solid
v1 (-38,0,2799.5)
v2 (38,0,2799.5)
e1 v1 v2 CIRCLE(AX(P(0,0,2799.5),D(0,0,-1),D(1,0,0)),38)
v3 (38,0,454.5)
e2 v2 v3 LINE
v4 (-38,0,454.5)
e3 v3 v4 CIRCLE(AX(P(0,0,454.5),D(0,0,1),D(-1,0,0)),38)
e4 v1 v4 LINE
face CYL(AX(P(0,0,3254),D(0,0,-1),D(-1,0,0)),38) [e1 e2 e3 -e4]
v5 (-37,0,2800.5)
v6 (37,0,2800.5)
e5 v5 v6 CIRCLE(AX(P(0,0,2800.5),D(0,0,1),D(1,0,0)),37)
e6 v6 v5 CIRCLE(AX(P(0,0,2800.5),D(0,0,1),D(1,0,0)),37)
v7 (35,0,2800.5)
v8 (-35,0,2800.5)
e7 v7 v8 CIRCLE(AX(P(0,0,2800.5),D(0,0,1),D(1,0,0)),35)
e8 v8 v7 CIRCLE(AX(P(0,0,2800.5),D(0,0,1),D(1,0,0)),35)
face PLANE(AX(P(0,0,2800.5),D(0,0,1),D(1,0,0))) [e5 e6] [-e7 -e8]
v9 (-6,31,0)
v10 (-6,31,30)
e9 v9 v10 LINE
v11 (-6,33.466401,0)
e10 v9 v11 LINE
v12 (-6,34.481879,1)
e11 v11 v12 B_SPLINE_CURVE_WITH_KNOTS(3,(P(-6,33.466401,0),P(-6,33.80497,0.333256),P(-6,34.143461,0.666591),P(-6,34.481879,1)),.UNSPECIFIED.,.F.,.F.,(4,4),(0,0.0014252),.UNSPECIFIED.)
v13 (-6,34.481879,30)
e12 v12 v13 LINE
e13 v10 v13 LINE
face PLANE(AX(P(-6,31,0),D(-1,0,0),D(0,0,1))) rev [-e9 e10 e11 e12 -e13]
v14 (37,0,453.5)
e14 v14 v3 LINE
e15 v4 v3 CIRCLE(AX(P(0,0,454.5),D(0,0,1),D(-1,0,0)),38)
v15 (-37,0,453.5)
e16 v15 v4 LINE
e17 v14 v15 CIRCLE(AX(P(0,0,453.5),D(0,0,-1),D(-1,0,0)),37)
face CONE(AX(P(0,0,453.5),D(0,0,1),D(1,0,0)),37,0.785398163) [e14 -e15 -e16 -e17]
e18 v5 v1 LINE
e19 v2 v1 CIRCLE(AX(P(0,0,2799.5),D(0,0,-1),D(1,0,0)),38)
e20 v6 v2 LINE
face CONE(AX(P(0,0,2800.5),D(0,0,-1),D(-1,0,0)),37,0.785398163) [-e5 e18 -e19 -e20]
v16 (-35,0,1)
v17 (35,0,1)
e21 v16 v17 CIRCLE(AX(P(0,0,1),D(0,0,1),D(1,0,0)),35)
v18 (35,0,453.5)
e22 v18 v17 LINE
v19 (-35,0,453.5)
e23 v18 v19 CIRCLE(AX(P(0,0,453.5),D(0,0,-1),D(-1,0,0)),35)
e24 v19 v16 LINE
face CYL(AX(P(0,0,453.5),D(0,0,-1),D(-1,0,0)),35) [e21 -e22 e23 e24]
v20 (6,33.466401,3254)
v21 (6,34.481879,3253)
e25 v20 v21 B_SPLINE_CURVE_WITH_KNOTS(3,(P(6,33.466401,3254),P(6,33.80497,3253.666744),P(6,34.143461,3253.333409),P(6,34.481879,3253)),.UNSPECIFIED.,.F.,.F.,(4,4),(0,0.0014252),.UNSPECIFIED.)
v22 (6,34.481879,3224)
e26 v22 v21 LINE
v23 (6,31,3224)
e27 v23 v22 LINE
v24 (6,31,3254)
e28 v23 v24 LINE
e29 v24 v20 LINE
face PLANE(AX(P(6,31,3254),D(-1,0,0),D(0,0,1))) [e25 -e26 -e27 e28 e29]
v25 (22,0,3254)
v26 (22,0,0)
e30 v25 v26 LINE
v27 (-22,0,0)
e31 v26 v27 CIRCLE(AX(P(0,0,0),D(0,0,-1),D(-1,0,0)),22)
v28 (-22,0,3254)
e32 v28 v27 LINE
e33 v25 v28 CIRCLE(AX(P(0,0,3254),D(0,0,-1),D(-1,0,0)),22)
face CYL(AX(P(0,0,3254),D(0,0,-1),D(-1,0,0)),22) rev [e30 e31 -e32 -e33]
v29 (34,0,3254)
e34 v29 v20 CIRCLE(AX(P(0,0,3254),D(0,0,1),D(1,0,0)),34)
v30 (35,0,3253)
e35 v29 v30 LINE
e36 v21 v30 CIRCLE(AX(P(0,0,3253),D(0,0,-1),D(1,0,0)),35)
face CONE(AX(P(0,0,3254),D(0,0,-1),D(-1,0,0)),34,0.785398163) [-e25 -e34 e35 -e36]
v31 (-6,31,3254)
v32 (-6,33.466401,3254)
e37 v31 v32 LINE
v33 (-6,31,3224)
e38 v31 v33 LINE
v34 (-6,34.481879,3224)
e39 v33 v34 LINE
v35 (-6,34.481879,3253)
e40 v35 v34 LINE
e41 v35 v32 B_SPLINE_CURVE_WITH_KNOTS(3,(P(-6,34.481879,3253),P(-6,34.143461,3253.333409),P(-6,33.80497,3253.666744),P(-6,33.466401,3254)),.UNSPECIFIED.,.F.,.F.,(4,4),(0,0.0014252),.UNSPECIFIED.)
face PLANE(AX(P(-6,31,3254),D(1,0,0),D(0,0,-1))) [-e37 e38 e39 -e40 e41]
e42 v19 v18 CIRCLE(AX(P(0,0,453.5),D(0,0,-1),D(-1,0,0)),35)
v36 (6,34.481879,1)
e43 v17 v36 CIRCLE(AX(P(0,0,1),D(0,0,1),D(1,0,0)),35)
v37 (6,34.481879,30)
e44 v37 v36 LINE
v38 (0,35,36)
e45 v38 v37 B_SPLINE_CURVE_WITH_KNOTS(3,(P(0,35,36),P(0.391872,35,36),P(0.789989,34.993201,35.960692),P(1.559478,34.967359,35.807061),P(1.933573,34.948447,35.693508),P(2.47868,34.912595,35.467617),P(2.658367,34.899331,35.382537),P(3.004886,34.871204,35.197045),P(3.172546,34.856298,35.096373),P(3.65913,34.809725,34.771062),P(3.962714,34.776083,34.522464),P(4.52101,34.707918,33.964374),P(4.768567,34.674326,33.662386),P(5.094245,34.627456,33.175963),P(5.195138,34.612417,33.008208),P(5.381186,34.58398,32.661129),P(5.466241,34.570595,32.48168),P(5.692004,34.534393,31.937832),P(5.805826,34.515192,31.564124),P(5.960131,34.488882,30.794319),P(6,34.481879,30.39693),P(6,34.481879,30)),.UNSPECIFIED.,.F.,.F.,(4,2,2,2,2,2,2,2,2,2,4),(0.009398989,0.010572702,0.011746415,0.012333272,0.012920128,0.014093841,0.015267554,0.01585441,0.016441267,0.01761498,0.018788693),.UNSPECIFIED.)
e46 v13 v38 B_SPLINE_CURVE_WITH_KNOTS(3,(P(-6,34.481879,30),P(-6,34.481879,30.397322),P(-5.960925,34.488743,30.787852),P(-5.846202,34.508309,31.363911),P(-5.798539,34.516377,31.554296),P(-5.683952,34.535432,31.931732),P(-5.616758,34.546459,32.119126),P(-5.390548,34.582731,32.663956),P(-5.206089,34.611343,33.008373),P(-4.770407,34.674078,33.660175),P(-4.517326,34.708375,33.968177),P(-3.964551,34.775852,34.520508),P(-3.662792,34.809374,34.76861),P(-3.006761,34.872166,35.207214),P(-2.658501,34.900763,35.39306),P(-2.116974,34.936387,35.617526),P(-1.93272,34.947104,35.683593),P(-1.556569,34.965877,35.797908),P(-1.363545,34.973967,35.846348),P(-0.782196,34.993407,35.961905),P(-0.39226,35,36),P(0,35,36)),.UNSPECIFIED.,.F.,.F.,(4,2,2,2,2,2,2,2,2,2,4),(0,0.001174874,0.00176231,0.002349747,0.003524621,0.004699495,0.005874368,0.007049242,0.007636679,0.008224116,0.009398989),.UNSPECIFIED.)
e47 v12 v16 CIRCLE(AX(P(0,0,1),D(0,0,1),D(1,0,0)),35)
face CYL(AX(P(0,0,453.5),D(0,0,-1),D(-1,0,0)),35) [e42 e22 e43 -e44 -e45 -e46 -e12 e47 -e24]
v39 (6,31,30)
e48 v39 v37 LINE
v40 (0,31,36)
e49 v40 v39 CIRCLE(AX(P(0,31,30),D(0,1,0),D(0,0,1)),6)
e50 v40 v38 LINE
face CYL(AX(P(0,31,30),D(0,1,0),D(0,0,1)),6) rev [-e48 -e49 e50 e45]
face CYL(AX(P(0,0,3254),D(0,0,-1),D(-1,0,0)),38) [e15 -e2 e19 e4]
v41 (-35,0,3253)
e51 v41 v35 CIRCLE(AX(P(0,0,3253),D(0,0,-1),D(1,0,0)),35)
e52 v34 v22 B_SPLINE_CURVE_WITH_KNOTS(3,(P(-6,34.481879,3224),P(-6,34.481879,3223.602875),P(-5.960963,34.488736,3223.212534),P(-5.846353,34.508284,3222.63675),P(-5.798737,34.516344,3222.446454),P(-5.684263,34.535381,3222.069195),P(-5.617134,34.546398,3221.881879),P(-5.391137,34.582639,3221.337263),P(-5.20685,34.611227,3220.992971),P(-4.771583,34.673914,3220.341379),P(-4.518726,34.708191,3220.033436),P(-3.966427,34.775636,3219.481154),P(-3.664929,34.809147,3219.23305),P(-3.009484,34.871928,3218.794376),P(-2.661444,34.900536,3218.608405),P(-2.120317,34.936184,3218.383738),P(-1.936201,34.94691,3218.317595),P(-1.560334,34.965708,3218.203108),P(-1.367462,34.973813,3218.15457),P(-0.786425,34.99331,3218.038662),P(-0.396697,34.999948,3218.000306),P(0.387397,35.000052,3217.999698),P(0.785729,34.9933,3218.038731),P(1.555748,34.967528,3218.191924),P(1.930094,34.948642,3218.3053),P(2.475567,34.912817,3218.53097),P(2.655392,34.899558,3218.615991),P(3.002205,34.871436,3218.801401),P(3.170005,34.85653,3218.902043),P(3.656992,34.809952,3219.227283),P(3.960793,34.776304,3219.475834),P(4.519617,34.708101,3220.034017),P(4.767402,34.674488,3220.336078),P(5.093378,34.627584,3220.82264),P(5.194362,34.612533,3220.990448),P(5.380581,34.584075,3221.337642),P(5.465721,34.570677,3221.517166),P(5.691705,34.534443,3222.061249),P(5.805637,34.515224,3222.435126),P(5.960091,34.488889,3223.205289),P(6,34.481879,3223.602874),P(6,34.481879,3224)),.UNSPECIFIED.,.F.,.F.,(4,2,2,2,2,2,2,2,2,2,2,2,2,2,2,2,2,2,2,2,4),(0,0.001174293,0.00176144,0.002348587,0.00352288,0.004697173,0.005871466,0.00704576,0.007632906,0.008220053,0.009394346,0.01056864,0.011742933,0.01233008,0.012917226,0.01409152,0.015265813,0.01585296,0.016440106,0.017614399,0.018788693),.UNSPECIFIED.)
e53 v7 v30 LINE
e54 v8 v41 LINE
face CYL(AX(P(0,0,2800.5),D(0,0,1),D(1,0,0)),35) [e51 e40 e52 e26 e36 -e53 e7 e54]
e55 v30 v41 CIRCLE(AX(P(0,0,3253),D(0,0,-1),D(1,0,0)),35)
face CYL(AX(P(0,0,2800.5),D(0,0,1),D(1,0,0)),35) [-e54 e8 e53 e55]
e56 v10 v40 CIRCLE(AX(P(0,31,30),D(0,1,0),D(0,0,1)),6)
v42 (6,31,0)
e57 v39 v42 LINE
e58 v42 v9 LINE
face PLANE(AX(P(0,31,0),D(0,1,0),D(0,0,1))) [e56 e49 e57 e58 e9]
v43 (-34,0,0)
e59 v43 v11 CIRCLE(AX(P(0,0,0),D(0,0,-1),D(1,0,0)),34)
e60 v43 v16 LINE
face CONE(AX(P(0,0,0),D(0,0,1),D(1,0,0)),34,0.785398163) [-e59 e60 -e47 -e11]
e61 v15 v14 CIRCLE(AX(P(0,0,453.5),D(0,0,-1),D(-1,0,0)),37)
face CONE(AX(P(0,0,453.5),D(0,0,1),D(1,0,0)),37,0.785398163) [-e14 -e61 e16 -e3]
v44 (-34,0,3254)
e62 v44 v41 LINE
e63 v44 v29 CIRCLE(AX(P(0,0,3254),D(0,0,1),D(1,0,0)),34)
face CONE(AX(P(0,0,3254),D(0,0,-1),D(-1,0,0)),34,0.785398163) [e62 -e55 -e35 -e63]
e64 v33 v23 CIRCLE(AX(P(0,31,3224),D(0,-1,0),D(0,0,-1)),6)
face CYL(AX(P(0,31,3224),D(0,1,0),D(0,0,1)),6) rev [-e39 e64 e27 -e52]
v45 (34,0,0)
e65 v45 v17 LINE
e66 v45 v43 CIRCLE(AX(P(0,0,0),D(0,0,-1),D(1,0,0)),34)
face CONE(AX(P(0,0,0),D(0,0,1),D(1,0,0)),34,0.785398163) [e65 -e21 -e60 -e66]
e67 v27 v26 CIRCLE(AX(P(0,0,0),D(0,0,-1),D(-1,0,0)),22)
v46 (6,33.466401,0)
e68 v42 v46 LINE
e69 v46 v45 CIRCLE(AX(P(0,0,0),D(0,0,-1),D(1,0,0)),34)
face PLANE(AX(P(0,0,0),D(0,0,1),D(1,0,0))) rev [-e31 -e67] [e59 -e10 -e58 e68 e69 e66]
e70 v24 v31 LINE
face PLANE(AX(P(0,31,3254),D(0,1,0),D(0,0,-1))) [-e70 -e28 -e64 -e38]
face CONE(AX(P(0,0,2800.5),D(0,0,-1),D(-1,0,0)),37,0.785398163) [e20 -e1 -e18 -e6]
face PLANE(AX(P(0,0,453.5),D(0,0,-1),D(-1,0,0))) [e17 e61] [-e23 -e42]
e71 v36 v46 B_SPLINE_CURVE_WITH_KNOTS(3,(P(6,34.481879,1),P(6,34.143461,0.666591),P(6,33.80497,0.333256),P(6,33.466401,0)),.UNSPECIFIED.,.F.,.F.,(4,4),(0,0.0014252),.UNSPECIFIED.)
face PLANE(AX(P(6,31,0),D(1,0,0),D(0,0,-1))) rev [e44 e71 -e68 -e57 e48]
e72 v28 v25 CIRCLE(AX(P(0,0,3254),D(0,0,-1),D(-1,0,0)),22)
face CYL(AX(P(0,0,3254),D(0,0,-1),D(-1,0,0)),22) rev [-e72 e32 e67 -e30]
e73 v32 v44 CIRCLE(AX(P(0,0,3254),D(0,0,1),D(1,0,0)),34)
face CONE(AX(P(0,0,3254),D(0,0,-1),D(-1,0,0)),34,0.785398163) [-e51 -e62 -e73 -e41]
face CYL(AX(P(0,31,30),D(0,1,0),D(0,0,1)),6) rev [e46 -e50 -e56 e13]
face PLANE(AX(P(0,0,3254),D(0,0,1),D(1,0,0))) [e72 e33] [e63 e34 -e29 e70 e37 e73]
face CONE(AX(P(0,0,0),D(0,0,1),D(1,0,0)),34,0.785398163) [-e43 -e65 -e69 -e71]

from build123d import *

# Parameters (mm, degrees)
SKETCH1_R           = 38
BOSS_EXTRUDE1_DEPTH = 3254
SKETCH2_R           = 38
SKETCH2_R_2         = 35
CUT_EXTRUDE1_DEPTH  = 453.5
CUT_EXTRUDE2_START  = -453.5
SKETCH3_R           = 38
SKETCH3_R_2         = 35
CUT_EXTRUDE2_DEPTH  = 453.5
SKETCH5_R           = 22
CUT_EXTRUDE3_DEPTH  = 3255.44373127
CUT_EXTRUDE4_DEPTH  = 4
CHAMFER1_SIZE       = 1


with BuildPart() as part:
    # Sketch1 → Boss-Extrude1 (new body)
    with BuildSketch(Plane.XY):
        Circle(SKETCH1_R)
    extrude(amount=BOSS_EXTRUDE1_DEPTH)

    # Sketch2 → Cut-Extrude1 (cut)
    with BuildSketch(Plane(origin=(0, 0, 0), x_dir=(-1, 0, 0), z_dir=(0, 0, -1))):
        Circle(SKETCH2_R)
        Circle(SKETCH2_R_2, mode=Mode.SUBTRACT)
    extrude(amount=-CUT_EXTRUDE1_DEPTH, mode=Mode.SUBTRACT)

    # Sketch3 → Cut-Extrude2 (cut)
    with BuildSketch(Plane.XY.offset(3254).offset(CUT_EXTRUDE2_START)):
        with Locations(Location((0, 0, 0), (0, 0, 180))):
            Circle(SKETCH3_R)
        with Locations(Location((0, 0, 0), (0, 0, 180))):
            Circle(SKETCH3_R_2, mode=Mode.SUBTRACT)
    extrude(amount=CUT_EXTRUDE2_DEPTH, mode=Mode.SUBTRACT)

    # Sketch5 → Cut-Extrude3 (cut, through all)
    with BuildSketch(Plane(origin=(0, 0, 0), x_dir=(-1, 0, 0), z_dir=(0, 0, -1))):
        Circle(SKETCH5_R)
    extrude(amount=-CUT_EXTRUDE3_DEPTH, mode=Mode.SUBTRACT)

    # Sketch6 → Cut-Extrude4 (cut)
    with BuildSketch(Plane(origin=(0, 35, 0), x_dir=(1, 0, 0), z_dir=(0, 1, 0))):
        with BuildLine():
            Line((6, 0), (6, -30))
            ThreePointArc((6, -30), (0, -36), (-6, -30))
            Line((-6, -30), (-6, 0))
            ThreePointArc((-6, 0), (0, 6), (6, 0))
        make_face()
    cut_extrude4 = extrude(amount=-CUT_EXTRUDE4_DEPTH, mode=Mode.SUBTRACT)

    # Mirror1: Cut-Extrude4 across plane
    add(cut_extrude4.mirror(Plane(origin=(0, 0, 1627), x_dir=(1, 0, 0), z_dir=(0, 0, -1))), mode=Mode.SUBTRACT)

    # Chamfer1
    chamfer1_edges = [part.edges().sort_by_distance(p)[0] for p in [
        (-38, 0, 2800.5),
        (22.527760652, -26.786190472, 0),
        (22.527760652, -26.786190472, 3254),
        (-38, 0, 453.5),
    ]]
    chamfer(chamfer1_edges, length=CHAMFER1_SIZE)


solid = part.part
